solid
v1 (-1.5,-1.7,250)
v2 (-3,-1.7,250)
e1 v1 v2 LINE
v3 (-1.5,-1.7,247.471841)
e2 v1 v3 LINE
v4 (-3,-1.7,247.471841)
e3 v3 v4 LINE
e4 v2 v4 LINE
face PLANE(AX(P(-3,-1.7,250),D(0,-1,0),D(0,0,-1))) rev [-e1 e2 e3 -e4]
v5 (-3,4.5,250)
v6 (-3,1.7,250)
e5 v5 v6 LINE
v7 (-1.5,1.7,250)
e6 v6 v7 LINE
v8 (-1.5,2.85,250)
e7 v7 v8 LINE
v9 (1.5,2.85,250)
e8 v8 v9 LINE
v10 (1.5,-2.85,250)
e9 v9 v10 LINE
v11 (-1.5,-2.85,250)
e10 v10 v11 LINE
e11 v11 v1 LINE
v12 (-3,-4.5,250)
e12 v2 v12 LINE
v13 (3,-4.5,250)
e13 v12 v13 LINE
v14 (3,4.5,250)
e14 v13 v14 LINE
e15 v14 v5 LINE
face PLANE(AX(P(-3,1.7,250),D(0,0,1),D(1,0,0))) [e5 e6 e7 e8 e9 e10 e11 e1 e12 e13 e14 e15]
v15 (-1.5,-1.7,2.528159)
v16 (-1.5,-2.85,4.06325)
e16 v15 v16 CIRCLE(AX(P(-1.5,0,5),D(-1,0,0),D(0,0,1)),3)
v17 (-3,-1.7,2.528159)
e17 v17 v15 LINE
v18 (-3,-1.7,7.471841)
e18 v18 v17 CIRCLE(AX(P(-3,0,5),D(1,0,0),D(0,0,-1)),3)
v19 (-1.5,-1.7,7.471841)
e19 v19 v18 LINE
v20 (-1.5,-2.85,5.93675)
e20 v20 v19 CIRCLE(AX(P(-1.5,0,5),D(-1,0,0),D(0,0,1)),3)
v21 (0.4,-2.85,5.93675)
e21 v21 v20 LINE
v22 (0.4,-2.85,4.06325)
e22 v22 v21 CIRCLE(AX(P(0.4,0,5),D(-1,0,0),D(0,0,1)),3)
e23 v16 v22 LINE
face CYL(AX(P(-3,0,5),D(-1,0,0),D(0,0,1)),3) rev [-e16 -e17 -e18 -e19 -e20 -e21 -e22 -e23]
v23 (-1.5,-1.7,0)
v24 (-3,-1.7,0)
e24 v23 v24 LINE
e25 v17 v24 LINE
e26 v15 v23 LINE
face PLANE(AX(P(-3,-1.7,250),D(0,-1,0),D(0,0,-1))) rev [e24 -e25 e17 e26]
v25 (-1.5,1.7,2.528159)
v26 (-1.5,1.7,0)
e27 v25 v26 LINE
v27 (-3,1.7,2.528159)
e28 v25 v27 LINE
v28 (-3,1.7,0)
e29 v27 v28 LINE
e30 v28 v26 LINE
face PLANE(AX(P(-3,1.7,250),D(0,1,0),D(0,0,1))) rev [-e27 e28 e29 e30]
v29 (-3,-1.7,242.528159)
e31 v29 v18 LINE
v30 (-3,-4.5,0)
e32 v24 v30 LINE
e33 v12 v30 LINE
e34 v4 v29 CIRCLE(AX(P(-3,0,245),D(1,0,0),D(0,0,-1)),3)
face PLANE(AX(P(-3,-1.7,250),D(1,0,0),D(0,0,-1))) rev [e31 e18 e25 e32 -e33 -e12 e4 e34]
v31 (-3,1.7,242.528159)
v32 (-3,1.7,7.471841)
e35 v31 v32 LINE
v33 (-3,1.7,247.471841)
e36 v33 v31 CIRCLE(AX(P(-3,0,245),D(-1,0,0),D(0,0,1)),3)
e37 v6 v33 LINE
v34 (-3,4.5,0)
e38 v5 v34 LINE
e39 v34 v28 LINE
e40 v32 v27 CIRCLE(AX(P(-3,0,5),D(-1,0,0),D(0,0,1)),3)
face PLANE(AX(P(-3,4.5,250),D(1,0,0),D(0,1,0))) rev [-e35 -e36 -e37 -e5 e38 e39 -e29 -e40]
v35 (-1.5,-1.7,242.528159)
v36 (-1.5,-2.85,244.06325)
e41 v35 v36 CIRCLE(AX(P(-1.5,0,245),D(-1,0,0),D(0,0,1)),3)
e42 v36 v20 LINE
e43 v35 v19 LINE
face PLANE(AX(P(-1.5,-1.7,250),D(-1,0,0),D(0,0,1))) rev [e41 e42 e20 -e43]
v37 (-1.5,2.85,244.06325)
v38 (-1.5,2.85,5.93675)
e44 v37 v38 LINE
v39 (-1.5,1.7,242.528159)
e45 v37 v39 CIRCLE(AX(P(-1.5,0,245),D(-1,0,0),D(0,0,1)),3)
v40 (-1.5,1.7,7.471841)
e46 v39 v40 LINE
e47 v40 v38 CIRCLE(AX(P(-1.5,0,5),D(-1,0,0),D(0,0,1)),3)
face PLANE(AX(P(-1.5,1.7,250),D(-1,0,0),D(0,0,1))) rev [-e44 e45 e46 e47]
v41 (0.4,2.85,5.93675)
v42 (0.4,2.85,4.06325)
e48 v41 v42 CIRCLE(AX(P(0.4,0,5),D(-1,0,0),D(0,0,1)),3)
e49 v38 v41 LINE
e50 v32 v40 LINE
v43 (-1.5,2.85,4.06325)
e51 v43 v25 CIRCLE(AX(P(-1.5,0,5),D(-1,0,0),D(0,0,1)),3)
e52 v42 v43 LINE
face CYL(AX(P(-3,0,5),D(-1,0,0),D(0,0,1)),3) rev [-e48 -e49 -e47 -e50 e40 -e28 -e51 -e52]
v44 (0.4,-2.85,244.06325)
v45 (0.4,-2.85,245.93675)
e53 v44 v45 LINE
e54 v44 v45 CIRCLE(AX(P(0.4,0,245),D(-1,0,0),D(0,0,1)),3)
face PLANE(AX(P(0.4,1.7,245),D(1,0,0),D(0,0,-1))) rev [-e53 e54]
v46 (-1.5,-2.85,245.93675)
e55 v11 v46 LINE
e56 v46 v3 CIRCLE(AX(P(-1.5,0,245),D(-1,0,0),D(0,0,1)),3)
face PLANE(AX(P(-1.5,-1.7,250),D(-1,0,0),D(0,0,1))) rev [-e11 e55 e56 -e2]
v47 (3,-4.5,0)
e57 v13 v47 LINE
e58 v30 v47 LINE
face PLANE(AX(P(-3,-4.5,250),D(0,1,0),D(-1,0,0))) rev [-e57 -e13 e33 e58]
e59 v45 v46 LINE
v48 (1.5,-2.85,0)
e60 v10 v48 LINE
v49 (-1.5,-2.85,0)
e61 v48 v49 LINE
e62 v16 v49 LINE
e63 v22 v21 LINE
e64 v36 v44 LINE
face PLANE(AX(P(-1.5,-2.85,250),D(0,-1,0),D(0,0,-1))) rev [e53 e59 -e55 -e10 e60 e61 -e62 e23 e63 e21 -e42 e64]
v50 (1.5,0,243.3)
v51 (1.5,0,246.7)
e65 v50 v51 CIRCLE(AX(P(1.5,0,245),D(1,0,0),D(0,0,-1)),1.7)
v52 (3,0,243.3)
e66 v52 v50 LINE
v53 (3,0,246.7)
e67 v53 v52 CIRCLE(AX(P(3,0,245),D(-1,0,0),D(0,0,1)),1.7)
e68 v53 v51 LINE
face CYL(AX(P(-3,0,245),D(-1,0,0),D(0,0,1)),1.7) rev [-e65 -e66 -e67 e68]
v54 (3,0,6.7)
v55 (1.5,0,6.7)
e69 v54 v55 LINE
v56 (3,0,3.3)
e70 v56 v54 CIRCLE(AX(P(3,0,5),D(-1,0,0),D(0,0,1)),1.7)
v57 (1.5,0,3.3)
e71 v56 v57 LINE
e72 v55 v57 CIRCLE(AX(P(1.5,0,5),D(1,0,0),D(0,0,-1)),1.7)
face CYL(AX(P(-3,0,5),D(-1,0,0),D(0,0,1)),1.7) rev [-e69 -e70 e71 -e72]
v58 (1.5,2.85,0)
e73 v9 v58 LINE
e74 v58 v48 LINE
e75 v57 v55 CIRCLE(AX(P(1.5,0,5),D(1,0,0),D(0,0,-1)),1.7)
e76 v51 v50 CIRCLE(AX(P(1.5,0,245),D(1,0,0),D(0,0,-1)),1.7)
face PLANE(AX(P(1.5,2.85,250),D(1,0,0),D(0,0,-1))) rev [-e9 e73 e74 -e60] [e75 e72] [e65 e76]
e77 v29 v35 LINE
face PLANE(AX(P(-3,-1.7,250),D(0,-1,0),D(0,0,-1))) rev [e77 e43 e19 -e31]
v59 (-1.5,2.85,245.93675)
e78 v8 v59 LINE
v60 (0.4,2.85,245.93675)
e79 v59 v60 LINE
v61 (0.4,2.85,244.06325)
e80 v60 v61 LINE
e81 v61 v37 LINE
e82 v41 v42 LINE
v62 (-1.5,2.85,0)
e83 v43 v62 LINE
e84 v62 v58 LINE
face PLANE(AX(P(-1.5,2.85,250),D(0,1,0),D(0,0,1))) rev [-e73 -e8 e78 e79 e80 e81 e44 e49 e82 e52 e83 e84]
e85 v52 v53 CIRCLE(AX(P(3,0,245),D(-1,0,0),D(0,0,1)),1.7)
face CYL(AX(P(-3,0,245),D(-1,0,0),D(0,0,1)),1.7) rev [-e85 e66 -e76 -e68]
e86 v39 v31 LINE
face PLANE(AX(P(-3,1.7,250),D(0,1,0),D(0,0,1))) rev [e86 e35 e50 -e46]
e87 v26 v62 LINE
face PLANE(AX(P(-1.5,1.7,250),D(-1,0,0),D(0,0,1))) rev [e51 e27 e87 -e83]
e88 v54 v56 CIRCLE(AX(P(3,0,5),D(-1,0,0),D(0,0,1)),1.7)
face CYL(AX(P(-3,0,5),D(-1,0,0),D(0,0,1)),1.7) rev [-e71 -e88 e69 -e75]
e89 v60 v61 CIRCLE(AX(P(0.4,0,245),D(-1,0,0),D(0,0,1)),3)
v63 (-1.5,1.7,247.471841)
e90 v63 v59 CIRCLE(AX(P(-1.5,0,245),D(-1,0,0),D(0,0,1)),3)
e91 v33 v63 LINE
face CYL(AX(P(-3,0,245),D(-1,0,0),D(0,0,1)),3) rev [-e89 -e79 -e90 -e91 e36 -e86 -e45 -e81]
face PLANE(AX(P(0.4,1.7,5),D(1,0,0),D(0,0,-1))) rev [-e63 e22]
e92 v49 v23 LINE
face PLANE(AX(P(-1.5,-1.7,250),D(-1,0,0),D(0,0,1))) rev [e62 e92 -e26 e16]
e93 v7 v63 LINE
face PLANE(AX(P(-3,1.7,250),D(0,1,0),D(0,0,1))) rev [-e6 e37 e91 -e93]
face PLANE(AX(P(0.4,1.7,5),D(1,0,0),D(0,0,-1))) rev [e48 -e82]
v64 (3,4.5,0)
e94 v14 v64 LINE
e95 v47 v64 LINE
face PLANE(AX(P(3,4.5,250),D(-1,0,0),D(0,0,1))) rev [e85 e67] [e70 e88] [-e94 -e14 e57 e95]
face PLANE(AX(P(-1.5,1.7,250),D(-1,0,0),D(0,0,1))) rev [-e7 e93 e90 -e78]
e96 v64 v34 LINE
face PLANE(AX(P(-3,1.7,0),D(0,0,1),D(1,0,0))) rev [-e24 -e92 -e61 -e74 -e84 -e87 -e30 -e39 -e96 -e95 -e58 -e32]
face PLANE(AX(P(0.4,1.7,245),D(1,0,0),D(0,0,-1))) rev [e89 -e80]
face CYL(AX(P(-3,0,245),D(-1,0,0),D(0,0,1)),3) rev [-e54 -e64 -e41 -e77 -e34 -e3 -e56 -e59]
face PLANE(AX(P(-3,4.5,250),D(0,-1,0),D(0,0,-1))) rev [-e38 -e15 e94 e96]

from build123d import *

# Parameters (mm, degrees)
EXTRUDE_1_DEPTH           = 250
HOLE_WIZARD_1_D           = 3.4
HOLE_WIZARD_1_CBORE_D     = 6
HOLE_WIZARD_1_CBORE_DEPTH = 3.4


with BuildPart() as part:
    # 草圖1 → 伸長1 (new body)
    with BuildSketch(Plane.XY):
        Polygon((-3, 4.5), (3, 4.5), (3, -4.5), (-3, -4.5), (-3, -1.7), (-1.5, -1.7), (-1.5, -2.85), (1.5, -2.85), (1.5, 2.85), (-1.5, 2.85), (-1.5, 1.7), (-3, 1.7), align=None)
    extrude(amount=EXTRUDE_1_DEPTH)

    # 打孔尺寸(%根据)内六角圆柱头螺钉的类型1 (through all)
    with Locations(Plane.ZY.offset(3)):
        with Locations((245, 0), (5, 0)):
            CounterBoreHole(HOLE_WIZARD_1_D / 2, HOLE_WIZARD_1_CBORE_D / 2, HOLE_WIZARD_1_CBORE_DEPTH)


solid = part.part
